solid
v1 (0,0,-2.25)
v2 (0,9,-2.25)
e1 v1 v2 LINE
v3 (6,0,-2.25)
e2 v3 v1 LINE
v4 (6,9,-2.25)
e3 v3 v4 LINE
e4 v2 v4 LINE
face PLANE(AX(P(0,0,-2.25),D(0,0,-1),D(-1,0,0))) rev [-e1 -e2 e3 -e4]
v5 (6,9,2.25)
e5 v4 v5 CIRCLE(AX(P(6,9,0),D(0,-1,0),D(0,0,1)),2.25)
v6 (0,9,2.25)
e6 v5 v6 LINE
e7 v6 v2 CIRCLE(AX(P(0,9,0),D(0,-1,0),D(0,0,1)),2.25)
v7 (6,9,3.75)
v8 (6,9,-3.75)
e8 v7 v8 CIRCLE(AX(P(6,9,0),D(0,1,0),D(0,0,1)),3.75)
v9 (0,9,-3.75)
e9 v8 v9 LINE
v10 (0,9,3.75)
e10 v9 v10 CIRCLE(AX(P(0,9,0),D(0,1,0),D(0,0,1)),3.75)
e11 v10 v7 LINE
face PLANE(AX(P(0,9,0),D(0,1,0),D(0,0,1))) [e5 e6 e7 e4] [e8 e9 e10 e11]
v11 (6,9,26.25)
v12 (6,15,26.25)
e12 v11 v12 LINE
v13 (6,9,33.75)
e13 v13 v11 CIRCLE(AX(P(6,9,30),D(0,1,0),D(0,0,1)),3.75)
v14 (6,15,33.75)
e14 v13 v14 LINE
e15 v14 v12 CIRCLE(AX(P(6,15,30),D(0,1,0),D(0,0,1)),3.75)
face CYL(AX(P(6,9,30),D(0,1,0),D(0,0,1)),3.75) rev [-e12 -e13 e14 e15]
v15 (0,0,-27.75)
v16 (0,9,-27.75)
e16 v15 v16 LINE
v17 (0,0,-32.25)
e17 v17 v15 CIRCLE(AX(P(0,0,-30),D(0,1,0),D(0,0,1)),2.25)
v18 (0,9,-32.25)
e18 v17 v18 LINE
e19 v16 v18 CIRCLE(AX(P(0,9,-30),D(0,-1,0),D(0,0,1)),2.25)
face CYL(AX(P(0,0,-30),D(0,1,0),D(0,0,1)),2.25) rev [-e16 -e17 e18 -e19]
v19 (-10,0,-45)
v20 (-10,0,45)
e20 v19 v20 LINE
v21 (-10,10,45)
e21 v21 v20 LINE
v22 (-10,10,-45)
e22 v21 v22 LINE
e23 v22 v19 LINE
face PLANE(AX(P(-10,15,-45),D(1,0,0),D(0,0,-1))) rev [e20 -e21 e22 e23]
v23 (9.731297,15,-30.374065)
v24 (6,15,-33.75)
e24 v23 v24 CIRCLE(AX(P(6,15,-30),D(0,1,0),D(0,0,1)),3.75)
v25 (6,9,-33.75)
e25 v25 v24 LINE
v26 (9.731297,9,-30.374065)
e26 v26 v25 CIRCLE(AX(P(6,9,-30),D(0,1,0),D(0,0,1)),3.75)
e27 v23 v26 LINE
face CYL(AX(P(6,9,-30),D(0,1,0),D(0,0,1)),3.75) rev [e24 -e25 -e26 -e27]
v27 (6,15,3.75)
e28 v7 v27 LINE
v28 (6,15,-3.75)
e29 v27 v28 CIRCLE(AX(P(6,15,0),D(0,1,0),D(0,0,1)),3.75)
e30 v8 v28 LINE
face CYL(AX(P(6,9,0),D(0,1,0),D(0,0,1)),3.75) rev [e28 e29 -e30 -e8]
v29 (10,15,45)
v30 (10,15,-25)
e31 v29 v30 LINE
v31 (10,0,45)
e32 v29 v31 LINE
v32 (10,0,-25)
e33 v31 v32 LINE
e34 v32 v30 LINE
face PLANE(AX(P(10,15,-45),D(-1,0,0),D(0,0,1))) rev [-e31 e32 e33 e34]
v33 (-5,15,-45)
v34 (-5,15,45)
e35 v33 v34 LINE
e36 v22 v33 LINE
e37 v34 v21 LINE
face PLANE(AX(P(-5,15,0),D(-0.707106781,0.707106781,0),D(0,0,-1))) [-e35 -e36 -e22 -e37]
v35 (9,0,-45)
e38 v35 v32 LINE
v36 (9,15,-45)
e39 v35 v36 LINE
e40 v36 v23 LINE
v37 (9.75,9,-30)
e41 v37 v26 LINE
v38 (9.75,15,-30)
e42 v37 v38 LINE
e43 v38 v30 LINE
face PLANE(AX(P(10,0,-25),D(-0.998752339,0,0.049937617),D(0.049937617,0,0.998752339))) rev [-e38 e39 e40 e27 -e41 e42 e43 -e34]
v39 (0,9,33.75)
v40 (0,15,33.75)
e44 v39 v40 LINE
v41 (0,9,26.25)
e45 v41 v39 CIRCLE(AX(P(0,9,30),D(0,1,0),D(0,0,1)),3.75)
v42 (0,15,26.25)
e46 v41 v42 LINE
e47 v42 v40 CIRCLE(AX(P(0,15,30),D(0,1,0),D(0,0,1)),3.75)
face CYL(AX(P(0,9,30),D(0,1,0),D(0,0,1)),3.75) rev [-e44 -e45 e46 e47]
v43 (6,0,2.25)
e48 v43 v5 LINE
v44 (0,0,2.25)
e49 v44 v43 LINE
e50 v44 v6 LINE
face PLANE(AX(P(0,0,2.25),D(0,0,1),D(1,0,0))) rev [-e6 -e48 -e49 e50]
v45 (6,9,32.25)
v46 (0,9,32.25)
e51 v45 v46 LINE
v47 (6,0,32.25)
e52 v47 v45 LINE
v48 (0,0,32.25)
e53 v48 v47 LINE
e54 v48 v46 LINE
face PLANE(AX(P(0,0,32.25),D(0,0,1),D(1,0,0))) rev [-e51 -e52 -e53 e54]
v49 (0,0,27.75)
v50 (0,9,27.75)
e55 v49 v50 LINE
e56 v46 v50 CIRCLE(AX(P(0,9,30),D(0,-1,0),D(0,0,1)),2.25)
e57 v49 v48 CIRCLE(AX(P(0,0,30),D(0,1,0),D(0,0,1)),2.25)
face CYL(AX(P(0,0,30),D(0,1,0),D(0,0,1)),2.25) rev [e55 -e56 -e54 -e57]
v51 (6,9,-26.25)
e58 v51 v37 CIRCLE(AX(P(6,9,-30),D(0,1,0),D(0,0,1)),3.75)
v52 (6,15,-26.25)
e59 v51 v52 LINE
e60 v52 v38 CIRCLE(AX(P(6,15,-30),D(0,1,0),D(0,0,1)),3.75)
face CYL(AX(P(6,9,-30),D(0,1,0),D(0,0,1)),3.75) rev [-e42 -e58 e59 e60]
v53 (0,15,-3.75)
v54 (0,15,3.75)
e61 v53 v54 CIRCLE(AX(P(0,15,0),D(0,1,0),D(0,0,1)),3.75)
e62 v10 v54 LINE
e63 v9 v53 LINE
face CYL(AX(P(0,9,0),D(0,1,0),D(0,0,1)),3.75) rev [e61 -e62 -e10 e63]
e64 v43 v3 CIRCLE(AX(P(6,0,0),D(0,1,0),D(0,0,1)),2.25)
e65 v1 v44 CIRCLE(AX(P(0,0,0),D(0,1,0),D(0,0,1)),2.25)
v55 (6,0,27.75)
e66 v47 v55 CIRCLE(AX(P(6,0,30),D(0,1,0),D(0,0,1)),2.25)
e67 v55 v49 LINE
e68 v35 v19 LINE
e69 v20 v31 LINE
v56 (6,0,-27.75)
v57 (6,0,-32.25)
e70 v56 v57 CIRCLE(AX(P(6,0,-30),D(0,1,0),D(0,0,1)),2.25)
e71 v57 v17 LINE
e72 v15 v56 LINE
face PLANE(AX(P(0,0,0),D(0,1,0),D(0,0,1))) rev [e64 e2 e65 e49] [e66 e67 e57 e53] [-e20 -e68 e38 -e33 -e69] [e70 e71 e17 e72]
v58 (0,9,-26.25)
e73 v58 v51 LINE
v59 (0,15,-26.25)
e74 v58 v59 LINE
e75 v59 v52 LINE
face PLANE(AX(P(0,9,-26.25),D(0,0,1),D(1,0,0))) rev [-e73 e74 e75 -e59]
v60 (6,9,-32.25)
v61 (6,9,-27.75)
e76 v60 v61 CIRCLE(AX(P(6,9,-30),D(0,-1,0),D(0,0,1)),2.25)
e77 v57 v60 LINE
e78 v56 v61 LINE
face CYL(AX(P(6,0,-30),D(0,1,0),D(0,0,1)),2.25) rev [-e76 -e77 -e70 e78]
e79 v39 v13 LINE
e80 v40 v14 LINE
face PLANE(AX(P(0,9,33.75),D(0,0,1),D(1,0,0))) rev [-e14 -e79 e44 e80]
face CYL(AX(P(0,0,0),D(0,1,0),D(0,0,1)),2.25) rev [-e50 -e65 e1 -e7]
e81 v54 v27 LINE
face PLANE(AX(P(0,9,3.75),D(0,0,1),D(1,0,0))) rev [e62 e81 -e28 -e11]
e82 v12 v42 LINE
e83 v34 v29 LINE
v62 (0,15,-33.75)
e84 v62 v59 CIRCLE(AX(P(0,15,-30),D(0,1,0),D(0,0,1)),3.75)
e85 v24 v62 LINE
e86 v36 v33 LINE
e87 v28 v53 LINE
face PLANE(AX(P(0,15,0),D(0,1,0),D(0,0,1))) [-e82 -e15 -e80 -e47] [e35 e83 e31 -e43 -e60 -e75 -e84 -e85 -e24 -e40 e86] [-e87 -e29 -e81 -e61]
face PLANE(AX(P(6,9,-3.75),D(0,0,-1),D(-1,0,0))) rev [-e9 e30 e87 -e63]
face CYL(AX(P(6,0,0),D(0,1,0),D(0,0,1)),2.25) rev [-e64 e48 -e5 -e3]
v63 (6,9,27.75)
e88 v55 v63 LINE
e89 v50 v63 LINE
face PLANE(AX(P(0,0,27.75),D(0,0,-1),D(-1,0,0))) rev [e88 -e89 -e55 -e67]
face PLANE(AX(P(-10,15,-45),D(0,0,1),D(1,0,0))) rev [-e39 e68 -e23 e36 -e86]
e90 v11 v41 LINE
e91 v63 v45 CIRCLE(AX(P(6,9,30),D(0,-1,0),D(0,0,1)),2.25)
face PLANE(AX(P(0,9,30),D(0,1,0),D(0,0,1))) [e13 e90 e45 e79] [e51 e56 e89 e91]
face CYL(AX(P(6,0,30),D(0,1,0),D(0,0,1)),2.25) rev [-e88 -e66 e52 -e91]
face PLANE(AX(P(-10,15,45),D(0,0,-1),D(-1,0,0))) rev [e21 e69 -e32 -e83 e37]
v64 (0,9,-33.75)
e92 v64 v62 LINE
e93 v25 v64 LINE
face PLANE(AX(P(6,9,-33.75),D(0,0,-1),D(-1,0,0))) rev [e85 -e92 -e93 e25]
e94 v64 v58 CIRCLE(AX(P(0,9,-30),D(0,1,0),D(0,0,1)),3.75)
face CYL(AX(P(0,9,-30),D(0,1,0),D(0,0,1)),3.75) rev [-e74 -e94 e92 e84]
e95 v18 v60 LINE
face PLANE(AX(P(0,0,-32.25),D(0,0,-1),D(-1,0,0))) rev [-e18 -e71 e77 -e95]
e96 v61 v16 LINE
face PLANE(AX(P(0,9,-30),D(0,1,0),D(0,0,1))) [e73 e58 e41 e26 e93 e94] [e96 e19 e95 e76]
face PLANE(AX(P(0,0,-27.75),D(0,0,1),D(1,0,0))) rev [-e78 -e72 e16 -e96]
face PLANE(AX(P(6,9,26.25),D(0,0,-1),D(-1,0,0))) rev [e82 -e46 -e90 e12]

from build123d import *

# Parameters (mm, degrees)
SKETCH1_W                 = 20
SKETCH1_H                 = 90
BOSS_EXTRUDE1_DEPTH       = 15
CHAMFER1_SIZE             = 5
CUT_EXTRUDE1_DEPTH        = 49.476798574
CUT_EXTRUDE2_DEPTH        = 49.476798574
CUT_EXTRUDE3_DEPTH        = 6
LINEAR_PATTERN1_COUNT     = 2
LINEAR_PATTERN1_PITCH     = 30
LINEAR_PATTERN1_COL_COUNT = 2
LINEAR_PATTERN1_COL_PITCH = 30


with BuildPart() as part:
    # Sketch1 → Boss-Extrude1 (new body)
    with BuildSketch(Plane(origin=(0, 0, 0), x_dir=(1, 0, 0), z_dir=(0, 1, 0))):
        Rectangle(SKETCH1_W, SKETCH1_H)
    extrude(amount=BOSS_EXTRUDE1_DEPTH)

    # Chamfer1
    chamfer1_edges = [part.edges().sort_by_distance(p)[0] for p in [
        (-10, 15, 0),
    ]]
    chamfer(chamfer1_edges, length=CHAMFER1_SIZE)

    # Sketch2 → Cut-Extrude1 (cut, through all)
    with BuildSketch(Plane(origin=(0, 15, 0), x_dir=(1, 0, 0), z_dir=(0, 1, 0))):
        Polygon((10, 25), (9, 45), (10, 45), align=None)
    extrude(amount=-CUT_EXTRUDE1_DEPTH, mode=Mode.SUBTRACT)

    # Sketch3 → Cut-Extrude2 (cut, through all)
    with BuildSketch(Plane(origin=(0, 15, 0), x_dir=(1, 0, 0), z_dir=(0, 1, 0))):
        with BuildLine():
            Line((0, 2.25), (6, 2.25))
            ThreePointArc((6, 2.25), (8.25, 0), (6, -2.25))
            Line((6, -2.25), (0, -2.25))
            ThreePointArc((0, -2.25), (-2.25, 0), (0, 2.25))
        make_face()
    cut_extrude2 = extrude(amount=-CUT_EXTRUDE2_DEPTH, mode=Mode.SUBTRACT)

    # Sketch4 → Cut-Extrude3 (cut)
    with BuildSketch(Plane(origin=(0, 15, 0), x_dir=(1, 0, 0), z_dir=(0, 1, 0))):
        with BuildLine():
            Line((0, -3.75), (6, -3.75))
            ThreePointArc((6, -3.75), (9.75, 0), (6, 3.75))
            Line((6, 3.75), (0, 3.75))
            ThreePointArc((0, 3.75), (-3.75, 0), (0, -3.75))
        make_face()
    cut_extrude3 = extrude(amount=-CUT_EXTRUDE3_DEPTH, mode=Mode.SUBTRACT)

    # Linear pattern1: Cut-Extrude2, Cut-Extrude3 ×2
    with Locations(*[(0, 0, i * LINEAR_PATTERN1_PITCH) for i in range(1, LINEAR_PATTERN1_COUNT)]):
        add(cut_extrude2, mode=Mode.SUBTRACT)
        add(cut_extrude3, mode=Mode.SUBTRACT)

    # Linear pattern1 col: Cut-Extrude2, Cut-Extrude3 ×2
    with Locations(*[(0, 0, -i * LINEAR_PATTERN1_COL_PITCH) for i in range(1, LINEAR_PATTERN1_COL_COUNT)]):
        add(cut_extrude2, mode=Mode.SUBTRACT)
        add(cut_extrude3, mode=Mode.SUBTRACT)


solid = part.part
